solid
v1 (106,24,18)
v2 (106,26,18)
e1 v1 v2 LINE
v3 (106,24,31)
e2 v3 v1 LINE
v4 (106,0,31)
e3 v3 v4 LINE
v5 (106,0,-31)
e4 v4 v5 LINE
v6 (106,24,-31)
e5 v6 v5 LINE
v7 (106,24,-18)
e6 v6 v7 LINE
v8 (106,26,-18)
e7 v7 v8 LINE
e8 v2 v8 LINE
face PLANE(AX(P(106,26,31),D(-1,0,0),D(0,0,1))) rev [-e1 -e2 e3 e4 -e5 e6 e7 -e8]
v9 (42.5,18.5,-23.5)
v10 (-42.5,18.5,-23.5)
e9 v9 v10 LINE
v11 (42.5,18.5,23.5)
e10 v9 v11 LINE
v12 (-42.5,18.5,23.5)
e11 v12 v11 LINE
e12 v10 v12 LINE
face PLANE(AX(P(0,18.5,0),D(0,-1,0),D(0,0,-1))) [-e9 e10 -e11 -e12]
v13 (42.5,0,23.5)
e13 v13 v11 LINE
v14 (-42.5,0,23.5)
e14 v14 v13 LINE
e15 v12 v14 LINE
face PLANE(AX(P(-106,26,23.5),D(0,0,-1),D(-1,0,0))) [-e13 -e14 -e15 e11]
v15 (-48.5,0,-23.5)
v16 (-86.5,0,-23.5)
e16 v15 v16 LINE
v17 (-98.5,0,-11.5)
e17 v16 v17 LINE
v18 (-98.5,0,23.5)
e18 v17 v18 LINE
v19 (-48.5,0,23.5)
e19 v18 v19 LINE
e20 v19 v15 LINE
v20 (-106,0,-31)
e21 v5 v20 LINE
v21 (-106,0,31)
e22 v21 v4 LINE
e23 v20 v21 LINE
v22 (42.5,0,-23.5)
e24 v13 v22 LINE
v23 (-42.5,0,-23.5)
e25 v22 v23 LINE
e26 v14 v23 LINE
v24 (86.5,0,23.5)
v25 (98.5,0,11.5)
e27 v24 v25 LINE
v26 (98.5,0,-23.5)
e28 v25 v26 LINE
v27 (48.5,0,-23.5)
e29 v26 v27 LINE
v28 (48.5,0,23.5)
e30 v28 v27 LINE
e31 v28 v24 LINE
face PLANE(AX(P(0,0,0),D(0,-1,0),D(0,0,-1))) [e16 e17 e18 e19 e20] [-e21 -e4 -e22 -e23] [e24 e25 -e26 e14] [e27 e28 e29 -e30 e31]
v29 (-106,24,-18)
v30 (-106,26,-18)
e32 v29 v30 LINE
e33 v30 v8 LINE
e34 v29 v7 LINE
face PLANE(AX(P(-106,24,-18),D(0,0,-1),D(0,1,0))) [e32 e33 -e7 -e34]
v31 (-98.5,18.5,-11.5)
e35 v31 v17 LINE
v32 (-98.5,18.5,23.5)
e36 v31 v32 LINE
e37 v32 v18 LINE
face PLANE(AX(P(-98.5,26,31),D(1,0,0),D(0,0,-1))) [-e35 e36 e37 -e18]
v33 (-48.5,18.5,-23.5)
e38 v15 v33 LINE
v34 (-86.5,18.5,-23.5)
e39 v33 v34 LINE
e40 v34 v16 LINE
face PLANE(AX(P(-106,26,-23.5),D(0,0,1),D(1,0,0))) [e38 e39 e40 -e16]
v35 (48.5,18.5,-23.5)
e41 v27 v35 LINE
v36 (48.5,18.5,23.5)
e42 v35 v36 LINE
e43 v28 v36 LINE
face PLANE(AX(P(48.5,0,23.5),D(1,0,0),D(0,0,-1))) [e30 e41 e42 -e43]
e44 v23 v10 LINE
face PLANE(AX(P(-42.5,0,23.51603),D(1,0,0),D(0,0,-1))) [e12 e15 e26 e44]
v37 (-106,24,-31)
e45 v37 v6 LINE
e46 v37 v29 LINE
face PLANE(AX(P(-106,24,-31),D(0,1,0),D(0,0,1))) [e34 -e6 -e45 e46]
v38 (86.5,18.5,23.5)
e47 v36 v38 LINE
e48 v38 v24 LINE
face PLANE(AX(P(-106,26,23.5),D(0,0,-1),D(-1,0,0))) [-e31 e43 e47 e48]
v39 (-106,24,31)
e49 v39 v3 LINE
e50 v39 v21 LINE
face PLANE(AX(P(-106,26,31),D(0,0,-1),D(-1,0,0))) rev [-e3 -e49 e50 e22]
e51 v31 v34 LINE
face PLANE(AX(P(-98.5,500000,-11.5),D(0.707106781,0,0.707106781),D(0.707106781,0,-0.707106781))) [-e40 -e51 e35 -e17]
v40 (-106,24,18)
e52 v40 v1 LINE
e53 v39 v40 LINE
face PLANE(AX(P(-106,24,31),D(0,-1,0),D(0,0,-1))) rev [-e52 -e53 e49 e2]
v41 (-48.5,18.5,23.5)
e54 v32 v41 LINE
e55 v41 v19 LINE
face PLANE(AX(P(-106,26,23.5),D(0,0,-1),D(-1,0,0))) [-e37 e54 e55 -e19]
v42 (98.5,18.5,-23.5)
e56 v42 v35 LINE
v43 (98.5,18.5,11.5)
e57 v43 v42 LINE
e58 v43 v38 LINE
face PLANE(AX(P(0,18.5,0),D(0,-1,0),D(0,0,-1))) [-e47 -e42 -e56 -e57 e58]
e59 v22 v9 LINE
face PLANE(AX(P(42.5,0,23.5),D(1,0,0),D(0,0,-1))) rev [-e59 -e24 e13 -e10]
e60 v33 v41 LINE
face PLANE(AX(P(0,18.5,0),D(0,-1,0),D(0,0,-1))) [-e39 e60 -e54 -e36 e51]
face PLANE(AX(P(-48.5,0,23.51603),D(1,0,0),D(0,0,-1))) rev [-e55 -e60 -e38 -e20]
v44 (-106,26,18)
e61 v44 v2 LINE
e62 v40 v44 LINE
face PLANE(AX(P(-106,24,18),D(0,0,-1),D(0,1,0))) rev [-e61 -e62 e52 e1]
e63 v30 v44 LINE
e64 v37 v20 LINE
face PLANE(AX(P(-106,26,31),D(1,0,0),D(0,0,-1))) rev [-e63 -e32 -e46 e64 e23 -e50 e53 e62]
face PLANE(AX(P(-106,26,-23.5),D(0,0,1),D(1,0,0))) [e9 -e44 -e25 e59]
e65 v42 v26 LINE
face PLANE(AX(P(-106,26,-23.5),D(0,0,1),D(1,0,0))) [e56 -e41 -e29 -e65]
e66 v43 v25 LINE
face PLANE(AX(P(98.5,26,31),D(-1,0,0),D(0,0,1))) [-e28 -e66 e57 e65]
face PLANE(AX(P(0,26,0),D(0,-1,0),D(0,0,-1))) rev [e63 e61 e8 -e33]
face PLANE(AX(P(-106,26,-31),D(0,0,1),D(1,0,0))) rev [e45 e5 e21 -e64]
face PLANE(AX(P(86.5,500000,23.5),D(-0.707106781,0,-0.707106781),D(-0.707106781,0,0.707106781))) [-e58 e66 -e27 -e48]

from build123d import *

# Parameters (mm, degrees)
SKETCH1_W           = 212
SKETCH1_H           = 62
BOSS_EXTRUDE1_DEPTH = 26
SHELL1_T            = -7.5
SKETCH2_W           = 13
SKETCH2_H           = 2
CUT_EXTRUDE2_DEPTH  = 216.826319062
RIB1_REACH          = 115.459
SKETCH3_WALLS_W     = 6
SKETCH3_WALLS_H     = 275.918487568
SKETCH3_WALLS_H_2   = 275.934517232
BOSS_EXTRUDE2_REACH = 115.459


with BuildPart() as part:
    # Sketch1 → Boss-Extrude1 (new body)
    with BuildSketch(Plane(origin=(0, 0, 0), x_dir=(1, 0, 0), z_dir=(0, 1, 0))):
        Rectangle(SKETCH1_W, SKETCH1_H)
    extrude(amount=BOSS_EXTRUDE1_DEPTH)

    # Shell1
    shell1_openings = [part.faces().sort_by_distance(p)[0] for p in [
        (0, 0, 0),
    ]]
    offset(amount=SHELL1_T, openings=shell1_openings, kind=Kind.INTERSECTION)

    # Sketch2 → Cut-Extrude2 (cut, through all)
    with BuildSketch(Plane(origin=(106, 0, 0), x_dir=(0, 0, -1), z_dir=(1, 0, 0))):
        with Locations((24.5, 25)):
            Rectangle(SKETCH2_W, SKETCH2_H)
        with Locations((-24.5, 25)):
            Rectangle(SKETCH2_W, SKETCH2_H)
    extrude(amount=-CUT_EXTRUDE2_DEPTH, mode=Mode.SUBTRACT)

    # Sketch3 walls → Rib1 (add, up to next)
    with BuildSketch(Plane.XZ, mode=Mode.PRIVATE) as rib1_sk1:
        with Locations((45.5, 0)):
            Rectangle(SKETCH3_WALLS_W, SKETCH3_WALLS_H)
    rib1_tool1 = extrude(rib1_sk1.sketch, amount=-RIB1_REACH, mode=Mode.PRIVATE) - part.part
    # Sketch3 walls → Rib1 (add, up to next)
    with BuildSketch(Plane.XZ, mode=Mode.PRIVATE) as rib1_sk2:
        with Locations((-45.5, 0.008014832)):
            Rectangle(SKETCH3_WALLS_W, SKETCH3_WALLS_H_2)
    rib1_tool2 = extrude(rib1_sk2.sketch, amount=-RIB1_REACH, mode=Mode.PRIVATE) - part.part
    add(rib1_tool1.solids().sort_by_distance((45.5, 0, 0))[0])
    add(rib1_tool2.solids().sort_by_distance((-45.5, 0, 0.008014832))[0])

    # Sketch4 → Boss-Extrude2 (add, up to next)
    with BuildSketch(Plane.XZ, mode=Mode.PRIVATE) as boss_extrude2_sk1:
        Polygon((86.5, 23.5), (98.5, 11.5), (98.5, 23.5), align=None)
    boss_extrude2_tool1 = extrude(boss_extrude2_sk1.sketch, amount=-BOSS_EXTRUDE2_REACH, mode=Mode.PRIVATE) - part.part
    # Sketch4 → Boss-Extrude2 (add, up to next)
    with BuildSketch(Plane.XZ, mode=Mode.PRIVATE) as boss_extrude2_sk2:
        Polygon((-98.5, -11.5), (-86.5, -23.5), (-98.5, -23.5), align=None)
    boss_extrude2_tool2 = extrude(boss_extrude2_sk2.sketch, amount=-BOSS_EXTRUDE2_REACH, mode=Mode.PRIVATE) - part.part
    add(boss_extrude2_tool1.solids().sort_by_distance((94.5, 0, 19.5))[0])
    add(boss_extrude2_tool2.solids().sort_by_distance((-94.5, 0, -19.5))[0])


solid = part.part
